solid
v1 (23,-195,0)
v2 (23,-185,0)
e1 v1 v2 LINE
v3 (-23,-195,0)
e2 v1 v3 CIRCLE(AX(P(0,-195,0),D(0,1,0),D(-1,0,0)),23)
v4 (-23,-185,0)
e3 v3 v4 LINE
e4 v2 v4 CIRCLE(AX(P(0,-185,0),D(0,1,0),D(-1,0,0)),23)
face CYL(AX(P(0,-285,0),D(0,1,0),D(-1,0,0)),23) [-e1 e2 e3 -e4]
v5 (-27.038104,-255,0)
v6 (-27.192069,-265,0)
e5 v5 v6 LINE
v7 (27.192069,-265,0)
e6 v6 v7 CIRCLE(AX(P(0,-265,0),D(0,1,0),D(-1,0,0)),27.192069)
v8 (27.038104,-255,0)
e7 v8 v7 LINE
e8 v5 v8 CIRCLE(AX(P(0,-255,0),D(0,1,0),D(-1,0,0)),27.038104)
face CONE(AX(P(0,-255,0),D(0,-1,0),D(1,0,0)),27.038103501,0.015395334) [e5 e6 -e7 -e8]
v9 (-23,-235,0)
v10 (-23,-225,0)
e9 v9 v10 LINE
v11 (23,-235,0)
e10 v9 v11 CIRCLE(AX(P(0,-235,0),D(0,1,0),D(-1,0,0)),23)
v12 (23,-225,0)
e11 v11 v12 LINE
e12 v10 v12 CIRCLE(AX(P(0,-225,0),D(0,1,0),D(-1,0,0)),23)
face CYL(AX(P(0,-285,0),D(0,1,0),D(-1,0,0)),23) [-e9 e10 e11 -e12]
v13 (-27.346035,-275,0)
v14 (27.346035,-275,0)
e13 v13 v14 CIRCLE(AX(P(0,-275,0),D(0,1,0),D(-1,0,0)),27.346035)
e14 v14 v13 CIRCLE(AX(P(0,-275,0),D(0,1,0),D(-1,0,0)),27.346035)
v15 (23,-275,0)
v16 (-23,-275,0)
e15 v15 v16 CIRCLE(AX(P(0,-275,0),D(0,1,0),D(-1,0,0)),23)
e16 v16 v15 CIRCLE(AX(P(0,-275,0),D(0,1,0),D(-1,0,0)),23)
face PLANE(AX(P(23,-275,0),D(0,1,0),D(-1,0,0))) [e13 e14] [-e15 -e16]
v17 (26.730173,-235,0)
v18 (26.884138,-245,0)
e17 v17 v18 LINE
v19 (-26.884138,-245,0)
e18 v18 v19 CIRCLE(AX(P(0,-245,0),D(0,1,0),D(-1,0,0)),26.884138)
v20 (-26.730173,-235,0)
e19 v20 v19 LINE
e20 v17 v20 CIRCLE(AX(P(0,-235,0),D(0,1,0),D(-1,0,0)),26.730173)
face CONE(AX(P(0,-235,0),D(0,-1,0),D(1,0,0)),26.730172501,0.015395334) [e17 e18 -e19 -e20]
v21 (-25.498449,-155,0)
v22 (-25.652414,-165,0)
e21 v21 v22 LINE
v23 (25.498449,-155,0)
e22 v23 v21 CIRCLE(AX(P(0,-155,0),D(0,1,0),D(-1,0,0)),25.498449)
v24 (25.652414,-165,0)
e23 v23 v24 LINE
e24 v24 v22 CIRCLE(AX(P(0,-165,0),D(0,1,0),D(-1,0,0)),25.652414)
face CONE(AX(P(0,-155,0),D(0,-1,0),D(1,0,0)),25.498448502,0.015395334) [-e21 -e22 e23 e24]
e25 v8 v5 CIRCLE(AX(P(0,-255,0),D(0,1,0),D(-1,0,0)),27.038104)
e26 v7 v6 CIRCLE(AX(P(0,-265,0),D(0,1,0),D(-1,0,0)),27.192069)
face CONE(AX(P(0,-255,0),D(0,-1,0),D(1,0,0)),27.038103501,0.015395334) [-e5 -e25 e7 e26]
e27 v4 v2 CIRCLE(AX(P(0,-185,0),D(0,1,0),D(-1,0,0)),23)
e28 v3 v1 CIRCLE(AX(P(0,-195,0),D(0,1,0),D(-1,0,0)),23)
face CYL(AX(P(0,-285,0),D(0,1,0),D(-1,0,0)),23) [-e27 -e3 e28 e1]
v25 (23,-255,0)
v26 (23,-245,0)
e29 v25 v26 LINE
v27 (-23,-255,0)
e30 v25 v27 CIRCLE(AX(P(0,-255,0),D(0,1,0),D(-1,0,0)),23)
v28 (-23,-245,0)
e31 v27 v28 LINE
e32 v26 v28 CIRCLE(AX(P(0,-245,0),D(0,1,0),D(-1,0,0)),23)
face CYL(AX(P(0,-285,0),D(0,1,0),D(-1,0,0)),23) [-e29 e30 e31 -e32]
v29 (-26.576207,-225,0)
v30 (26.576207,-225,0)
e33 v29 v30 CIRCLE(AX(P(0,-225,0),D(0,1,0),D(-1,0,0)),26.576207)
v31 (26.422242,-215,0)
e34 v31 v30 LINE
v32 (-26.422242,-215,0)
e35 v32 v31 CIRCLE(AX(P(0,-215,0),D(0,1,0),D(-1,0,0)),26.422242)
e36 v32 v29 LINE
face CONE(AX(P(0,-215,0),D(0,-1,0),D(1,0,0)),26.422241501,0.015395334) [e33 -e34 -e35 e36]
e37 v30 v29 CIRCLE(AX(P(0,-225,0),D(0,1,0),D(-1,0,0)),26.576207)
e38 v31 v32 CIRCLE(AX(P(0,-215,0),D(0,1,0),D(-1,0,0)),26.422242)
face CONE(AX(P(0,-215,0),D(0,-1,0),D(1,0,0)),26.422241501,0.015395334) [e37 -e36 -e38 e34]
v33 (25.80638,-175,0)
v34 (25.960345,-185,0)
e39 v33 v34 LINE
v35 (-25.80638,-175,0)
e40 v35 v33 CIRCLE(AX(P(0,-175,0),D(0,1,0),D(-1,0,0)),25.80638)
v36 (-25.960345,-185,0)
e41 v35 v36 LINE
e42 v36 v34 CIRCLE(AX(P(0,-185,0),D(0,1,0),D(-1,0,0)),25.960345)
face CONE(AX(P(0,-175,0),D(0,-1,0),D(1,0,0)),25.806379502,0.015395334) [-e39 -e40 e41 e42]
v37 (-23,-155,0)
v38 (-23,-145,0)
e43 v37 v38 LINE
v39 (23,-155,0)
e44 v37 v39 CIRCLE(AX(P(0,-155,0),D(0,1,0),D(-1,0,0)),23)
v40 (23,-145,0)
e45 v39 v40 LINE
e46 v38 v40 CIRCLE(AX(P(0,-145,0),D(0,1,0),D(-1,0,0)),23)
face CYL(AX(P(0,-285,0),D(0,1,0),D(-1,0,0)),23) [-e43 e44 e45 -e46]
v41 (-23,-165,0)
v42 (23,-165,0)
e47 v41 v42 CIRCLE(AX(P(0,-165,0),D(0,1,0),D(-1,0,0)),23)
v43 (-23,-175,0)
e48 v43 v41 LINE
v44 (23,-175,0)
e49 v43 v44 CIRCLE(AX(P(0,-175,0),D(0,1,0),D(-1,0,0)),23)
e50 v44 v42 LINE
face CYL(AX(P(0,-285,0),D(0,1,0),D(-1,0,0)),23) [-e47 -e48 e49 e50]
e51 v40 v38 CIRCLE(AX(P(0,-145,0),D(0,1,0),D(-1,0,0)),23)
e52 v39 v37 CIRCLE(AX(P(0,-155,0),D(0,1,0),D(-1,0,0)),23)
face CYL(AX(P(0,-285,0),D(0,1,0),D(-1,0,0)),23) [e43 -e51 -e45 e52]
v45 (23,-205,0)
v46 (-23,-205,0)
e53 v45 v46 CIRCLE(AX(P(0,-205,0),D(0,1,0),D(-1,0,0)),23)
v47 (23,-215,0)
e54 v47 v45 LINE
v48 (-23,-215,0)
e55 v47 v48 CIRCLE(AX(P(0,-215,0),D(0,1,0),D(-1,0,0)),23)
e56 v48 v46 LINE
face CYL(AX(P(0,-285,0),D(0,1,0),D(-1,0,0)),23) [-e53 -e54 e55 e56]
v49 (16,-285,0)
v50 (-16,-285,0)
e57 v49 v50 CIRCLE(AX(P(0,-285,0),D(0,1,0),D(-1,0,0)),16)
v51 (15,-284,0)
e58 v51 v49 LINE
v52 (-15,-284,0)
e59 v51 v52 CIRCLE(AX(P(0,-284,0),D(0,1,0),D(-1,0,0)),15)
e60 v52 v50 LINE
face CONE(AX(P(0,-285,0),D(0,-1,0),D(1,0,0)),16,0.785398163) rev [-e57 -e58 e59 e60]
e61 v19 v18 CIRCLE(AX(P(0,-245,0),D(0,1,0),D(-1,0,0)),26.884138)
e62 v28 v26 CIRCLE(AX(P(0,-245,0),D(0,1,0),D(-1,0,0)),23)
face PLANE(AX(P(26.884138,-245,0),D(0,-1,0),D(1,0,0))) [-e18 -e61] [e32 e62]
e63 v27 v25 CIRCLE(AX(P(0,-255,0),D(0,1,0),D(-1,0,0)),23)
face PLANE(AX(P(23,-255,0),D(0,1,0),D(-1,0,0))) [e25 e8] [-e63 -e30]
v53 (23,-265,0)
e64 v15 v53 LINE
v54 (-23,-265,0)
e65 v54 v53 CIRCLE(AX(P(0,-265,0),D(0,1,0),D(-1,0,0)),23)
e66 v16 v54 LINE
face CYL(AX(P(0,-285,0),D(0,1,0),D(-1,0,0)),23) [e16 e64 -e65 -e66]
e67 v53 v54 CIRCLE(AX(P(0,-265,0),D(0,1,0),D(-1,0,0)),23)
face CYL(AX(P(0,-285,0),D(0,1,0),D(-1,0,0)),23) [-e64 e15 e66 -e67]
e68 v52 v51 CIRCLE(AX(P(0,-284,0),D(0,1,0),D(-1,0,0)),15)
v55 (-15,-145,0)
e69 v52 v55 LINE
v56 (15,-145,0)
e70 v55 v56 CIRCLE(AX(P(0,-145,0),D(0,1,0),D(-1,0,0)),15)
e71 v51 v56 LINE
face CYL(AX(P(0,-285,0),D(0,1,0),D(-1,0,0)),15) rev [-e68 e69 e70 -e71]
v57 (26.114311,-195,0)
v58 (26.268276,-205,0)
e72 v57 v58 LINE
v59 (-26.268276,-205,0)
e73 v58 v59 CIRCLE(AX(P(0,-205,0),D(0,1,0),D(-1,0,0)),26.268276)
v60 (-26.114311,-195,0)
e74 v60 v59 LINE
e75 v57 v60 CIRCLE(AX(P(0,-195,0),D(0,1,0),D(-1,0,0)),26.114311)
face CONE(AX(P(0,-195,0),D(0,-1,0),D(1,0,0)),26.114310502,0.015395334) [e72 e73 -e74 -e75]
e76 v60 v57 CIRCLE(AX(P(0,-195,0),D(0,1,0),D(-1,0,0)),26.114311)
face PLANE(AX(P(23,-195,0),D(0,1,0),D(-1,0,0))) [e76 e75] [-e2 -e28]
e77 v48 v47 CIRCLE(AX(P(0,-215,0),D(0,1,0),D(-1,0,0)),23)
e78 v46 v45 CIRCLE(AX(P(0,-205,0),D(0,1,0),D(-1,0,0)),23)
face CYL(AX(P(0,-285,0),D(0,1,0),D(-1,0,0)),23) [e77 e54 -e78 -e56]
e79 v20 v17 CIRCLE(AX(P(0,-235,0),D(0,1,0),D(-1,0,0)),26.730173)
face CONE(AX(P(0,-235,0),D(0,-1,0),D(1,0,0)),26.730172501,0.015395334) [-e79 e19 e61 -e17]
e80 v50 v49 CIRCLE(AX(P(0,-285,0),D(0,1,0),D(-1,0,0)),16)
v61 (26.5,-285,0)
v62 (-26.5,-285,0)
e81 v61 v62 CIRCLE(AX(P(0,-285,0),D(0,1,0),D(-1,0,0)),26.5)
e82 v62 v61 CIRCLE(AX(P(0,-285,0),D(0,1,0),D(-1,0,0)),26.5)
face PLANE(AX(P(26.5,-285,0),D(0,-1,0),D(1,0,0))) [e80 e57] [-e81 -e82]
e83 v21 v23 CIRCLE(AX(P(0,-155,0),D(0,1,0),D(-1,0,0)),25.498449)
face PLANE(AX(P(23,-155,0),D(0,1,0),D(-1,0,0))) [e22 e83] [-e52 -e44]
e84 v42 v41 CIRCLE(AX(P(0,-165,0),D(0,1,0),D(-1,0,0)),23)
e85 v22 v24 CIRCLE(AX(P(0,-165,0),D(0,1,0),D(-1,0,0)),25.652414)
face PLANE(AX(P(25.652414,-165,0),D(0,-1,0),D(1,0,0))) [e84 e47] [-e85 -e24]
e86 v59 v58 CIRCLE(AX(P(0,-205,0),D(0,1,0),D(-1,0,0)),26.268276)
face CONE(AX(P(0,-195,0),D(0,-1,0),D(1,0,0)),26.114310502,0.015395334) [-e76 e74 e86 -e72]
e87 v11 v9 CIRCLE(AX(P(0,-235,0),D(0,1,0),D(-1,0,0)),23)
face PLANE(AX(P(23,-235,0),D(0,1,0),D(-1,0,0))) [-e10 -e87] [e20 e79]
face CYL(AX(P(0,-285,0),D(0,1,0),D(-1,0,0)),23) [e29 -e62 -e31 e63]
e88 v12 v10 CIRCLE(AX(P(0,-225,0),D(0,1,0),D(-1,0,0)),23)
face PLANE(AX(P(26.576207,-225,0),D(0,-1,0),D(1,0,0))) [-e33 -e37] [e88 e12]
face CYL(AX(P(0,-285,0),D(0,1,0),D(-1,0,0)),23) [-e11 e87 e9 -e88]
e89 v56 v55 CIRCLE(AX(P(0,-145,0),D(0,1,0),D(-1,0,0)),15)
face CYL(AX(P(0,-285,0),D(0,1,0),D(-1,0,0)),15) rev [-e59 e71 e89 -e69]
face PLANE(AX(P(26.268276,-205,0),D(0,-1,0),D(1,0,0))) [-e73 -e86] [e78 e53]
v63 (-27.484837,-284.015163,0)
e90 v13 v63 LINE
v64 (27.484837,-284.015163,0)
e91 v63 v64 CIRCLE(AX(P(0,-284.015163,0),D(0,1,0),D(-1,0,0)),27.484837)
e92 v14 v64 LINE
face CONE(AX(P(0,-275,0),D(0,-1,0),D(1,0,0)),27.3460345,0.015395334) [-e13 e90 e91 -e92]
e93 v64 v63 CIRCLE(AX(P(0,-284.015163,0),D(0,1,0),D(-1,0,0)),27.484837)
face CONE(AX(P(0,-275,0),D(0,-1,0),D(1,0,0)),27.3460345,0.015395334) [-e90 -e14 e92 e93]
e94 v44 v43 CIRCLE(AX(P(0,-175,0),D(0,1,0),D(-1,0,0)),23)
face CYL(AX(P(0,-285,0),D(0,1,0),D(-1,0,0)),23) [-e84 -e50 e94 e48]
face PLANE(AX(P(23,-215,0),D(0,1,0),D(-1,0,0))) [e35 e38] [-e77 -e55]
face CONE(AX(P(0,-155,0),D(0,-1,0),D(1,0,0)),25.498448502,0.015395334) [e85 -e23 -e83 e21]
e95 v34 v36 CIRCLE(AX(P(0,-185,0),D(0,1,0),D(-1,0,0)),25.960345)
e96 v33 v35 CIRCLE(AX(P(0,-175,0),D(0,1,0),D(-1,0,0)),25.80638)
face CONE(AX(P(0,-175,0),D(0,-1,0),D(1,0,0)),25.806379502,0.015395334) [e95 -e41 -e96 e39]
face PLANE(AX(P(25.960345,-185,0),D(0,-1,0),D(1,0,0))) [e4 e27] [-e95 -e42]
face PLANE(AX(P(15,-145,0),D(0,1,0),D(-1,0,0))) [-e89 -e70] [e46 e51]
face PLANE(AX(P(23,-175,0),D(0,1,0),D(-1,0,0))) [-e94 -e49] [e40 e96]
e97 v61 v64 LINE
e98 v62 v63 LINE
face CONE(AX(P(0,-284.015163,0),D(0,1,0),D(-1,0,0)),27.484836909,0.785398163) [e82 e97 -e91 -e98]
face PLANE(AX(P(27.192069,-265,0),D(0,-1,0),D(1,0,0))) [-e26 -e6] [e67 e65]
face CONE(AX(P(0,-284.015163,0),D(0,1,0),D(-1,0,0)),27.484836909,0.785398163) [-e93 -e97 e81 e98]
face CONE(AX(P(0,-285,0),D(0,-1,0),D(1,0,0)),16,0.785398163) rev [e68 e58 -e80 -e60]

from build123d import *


with BuildPart() as part:
    # 草图1 → 旋转1 (revolve)
    with BuildSketch(Plane(origin=(0, 0, 0), x_dir=(-1, 0, 0), z_dir=(0, 0, -1)), mode=Mode.PRIVATE) as revolve_1_sk:
        Polygon((-23, -215), (-26.422241501, -215), (-26.576207001, -225), (-23, -225), (-23, -235), (-26.730172501, -235), (-26.884138001, -245), (-23, -245), (-23, -255), (-27.038103501, -255), (-27.192069, -265), (-23, -265), (-23, -275), (-27.3460345, -275), (-27.484836909, -284.015163091), (-26.5, -285), (-16, -285), (-15, -284), (-15, -145), (-23, -145), (-23, -155), (-25.498448502, -155), (-25.652414002, -165), (-23, -165), (-23, -175), (-25.806379502, -175), (-25.960345002, -185), (-23, -185), (-23, -195), (-26.114310502, -195), (-26.268276001, -205), (-23, -205), align=None)
    revolve(revolve_1_sk.sketch.rotate(Axis((0, -285, 0), (0, 1, 0)), 180), axis=Axis((0, -285, 0), (0, 1, 0)))


solid = part.part
